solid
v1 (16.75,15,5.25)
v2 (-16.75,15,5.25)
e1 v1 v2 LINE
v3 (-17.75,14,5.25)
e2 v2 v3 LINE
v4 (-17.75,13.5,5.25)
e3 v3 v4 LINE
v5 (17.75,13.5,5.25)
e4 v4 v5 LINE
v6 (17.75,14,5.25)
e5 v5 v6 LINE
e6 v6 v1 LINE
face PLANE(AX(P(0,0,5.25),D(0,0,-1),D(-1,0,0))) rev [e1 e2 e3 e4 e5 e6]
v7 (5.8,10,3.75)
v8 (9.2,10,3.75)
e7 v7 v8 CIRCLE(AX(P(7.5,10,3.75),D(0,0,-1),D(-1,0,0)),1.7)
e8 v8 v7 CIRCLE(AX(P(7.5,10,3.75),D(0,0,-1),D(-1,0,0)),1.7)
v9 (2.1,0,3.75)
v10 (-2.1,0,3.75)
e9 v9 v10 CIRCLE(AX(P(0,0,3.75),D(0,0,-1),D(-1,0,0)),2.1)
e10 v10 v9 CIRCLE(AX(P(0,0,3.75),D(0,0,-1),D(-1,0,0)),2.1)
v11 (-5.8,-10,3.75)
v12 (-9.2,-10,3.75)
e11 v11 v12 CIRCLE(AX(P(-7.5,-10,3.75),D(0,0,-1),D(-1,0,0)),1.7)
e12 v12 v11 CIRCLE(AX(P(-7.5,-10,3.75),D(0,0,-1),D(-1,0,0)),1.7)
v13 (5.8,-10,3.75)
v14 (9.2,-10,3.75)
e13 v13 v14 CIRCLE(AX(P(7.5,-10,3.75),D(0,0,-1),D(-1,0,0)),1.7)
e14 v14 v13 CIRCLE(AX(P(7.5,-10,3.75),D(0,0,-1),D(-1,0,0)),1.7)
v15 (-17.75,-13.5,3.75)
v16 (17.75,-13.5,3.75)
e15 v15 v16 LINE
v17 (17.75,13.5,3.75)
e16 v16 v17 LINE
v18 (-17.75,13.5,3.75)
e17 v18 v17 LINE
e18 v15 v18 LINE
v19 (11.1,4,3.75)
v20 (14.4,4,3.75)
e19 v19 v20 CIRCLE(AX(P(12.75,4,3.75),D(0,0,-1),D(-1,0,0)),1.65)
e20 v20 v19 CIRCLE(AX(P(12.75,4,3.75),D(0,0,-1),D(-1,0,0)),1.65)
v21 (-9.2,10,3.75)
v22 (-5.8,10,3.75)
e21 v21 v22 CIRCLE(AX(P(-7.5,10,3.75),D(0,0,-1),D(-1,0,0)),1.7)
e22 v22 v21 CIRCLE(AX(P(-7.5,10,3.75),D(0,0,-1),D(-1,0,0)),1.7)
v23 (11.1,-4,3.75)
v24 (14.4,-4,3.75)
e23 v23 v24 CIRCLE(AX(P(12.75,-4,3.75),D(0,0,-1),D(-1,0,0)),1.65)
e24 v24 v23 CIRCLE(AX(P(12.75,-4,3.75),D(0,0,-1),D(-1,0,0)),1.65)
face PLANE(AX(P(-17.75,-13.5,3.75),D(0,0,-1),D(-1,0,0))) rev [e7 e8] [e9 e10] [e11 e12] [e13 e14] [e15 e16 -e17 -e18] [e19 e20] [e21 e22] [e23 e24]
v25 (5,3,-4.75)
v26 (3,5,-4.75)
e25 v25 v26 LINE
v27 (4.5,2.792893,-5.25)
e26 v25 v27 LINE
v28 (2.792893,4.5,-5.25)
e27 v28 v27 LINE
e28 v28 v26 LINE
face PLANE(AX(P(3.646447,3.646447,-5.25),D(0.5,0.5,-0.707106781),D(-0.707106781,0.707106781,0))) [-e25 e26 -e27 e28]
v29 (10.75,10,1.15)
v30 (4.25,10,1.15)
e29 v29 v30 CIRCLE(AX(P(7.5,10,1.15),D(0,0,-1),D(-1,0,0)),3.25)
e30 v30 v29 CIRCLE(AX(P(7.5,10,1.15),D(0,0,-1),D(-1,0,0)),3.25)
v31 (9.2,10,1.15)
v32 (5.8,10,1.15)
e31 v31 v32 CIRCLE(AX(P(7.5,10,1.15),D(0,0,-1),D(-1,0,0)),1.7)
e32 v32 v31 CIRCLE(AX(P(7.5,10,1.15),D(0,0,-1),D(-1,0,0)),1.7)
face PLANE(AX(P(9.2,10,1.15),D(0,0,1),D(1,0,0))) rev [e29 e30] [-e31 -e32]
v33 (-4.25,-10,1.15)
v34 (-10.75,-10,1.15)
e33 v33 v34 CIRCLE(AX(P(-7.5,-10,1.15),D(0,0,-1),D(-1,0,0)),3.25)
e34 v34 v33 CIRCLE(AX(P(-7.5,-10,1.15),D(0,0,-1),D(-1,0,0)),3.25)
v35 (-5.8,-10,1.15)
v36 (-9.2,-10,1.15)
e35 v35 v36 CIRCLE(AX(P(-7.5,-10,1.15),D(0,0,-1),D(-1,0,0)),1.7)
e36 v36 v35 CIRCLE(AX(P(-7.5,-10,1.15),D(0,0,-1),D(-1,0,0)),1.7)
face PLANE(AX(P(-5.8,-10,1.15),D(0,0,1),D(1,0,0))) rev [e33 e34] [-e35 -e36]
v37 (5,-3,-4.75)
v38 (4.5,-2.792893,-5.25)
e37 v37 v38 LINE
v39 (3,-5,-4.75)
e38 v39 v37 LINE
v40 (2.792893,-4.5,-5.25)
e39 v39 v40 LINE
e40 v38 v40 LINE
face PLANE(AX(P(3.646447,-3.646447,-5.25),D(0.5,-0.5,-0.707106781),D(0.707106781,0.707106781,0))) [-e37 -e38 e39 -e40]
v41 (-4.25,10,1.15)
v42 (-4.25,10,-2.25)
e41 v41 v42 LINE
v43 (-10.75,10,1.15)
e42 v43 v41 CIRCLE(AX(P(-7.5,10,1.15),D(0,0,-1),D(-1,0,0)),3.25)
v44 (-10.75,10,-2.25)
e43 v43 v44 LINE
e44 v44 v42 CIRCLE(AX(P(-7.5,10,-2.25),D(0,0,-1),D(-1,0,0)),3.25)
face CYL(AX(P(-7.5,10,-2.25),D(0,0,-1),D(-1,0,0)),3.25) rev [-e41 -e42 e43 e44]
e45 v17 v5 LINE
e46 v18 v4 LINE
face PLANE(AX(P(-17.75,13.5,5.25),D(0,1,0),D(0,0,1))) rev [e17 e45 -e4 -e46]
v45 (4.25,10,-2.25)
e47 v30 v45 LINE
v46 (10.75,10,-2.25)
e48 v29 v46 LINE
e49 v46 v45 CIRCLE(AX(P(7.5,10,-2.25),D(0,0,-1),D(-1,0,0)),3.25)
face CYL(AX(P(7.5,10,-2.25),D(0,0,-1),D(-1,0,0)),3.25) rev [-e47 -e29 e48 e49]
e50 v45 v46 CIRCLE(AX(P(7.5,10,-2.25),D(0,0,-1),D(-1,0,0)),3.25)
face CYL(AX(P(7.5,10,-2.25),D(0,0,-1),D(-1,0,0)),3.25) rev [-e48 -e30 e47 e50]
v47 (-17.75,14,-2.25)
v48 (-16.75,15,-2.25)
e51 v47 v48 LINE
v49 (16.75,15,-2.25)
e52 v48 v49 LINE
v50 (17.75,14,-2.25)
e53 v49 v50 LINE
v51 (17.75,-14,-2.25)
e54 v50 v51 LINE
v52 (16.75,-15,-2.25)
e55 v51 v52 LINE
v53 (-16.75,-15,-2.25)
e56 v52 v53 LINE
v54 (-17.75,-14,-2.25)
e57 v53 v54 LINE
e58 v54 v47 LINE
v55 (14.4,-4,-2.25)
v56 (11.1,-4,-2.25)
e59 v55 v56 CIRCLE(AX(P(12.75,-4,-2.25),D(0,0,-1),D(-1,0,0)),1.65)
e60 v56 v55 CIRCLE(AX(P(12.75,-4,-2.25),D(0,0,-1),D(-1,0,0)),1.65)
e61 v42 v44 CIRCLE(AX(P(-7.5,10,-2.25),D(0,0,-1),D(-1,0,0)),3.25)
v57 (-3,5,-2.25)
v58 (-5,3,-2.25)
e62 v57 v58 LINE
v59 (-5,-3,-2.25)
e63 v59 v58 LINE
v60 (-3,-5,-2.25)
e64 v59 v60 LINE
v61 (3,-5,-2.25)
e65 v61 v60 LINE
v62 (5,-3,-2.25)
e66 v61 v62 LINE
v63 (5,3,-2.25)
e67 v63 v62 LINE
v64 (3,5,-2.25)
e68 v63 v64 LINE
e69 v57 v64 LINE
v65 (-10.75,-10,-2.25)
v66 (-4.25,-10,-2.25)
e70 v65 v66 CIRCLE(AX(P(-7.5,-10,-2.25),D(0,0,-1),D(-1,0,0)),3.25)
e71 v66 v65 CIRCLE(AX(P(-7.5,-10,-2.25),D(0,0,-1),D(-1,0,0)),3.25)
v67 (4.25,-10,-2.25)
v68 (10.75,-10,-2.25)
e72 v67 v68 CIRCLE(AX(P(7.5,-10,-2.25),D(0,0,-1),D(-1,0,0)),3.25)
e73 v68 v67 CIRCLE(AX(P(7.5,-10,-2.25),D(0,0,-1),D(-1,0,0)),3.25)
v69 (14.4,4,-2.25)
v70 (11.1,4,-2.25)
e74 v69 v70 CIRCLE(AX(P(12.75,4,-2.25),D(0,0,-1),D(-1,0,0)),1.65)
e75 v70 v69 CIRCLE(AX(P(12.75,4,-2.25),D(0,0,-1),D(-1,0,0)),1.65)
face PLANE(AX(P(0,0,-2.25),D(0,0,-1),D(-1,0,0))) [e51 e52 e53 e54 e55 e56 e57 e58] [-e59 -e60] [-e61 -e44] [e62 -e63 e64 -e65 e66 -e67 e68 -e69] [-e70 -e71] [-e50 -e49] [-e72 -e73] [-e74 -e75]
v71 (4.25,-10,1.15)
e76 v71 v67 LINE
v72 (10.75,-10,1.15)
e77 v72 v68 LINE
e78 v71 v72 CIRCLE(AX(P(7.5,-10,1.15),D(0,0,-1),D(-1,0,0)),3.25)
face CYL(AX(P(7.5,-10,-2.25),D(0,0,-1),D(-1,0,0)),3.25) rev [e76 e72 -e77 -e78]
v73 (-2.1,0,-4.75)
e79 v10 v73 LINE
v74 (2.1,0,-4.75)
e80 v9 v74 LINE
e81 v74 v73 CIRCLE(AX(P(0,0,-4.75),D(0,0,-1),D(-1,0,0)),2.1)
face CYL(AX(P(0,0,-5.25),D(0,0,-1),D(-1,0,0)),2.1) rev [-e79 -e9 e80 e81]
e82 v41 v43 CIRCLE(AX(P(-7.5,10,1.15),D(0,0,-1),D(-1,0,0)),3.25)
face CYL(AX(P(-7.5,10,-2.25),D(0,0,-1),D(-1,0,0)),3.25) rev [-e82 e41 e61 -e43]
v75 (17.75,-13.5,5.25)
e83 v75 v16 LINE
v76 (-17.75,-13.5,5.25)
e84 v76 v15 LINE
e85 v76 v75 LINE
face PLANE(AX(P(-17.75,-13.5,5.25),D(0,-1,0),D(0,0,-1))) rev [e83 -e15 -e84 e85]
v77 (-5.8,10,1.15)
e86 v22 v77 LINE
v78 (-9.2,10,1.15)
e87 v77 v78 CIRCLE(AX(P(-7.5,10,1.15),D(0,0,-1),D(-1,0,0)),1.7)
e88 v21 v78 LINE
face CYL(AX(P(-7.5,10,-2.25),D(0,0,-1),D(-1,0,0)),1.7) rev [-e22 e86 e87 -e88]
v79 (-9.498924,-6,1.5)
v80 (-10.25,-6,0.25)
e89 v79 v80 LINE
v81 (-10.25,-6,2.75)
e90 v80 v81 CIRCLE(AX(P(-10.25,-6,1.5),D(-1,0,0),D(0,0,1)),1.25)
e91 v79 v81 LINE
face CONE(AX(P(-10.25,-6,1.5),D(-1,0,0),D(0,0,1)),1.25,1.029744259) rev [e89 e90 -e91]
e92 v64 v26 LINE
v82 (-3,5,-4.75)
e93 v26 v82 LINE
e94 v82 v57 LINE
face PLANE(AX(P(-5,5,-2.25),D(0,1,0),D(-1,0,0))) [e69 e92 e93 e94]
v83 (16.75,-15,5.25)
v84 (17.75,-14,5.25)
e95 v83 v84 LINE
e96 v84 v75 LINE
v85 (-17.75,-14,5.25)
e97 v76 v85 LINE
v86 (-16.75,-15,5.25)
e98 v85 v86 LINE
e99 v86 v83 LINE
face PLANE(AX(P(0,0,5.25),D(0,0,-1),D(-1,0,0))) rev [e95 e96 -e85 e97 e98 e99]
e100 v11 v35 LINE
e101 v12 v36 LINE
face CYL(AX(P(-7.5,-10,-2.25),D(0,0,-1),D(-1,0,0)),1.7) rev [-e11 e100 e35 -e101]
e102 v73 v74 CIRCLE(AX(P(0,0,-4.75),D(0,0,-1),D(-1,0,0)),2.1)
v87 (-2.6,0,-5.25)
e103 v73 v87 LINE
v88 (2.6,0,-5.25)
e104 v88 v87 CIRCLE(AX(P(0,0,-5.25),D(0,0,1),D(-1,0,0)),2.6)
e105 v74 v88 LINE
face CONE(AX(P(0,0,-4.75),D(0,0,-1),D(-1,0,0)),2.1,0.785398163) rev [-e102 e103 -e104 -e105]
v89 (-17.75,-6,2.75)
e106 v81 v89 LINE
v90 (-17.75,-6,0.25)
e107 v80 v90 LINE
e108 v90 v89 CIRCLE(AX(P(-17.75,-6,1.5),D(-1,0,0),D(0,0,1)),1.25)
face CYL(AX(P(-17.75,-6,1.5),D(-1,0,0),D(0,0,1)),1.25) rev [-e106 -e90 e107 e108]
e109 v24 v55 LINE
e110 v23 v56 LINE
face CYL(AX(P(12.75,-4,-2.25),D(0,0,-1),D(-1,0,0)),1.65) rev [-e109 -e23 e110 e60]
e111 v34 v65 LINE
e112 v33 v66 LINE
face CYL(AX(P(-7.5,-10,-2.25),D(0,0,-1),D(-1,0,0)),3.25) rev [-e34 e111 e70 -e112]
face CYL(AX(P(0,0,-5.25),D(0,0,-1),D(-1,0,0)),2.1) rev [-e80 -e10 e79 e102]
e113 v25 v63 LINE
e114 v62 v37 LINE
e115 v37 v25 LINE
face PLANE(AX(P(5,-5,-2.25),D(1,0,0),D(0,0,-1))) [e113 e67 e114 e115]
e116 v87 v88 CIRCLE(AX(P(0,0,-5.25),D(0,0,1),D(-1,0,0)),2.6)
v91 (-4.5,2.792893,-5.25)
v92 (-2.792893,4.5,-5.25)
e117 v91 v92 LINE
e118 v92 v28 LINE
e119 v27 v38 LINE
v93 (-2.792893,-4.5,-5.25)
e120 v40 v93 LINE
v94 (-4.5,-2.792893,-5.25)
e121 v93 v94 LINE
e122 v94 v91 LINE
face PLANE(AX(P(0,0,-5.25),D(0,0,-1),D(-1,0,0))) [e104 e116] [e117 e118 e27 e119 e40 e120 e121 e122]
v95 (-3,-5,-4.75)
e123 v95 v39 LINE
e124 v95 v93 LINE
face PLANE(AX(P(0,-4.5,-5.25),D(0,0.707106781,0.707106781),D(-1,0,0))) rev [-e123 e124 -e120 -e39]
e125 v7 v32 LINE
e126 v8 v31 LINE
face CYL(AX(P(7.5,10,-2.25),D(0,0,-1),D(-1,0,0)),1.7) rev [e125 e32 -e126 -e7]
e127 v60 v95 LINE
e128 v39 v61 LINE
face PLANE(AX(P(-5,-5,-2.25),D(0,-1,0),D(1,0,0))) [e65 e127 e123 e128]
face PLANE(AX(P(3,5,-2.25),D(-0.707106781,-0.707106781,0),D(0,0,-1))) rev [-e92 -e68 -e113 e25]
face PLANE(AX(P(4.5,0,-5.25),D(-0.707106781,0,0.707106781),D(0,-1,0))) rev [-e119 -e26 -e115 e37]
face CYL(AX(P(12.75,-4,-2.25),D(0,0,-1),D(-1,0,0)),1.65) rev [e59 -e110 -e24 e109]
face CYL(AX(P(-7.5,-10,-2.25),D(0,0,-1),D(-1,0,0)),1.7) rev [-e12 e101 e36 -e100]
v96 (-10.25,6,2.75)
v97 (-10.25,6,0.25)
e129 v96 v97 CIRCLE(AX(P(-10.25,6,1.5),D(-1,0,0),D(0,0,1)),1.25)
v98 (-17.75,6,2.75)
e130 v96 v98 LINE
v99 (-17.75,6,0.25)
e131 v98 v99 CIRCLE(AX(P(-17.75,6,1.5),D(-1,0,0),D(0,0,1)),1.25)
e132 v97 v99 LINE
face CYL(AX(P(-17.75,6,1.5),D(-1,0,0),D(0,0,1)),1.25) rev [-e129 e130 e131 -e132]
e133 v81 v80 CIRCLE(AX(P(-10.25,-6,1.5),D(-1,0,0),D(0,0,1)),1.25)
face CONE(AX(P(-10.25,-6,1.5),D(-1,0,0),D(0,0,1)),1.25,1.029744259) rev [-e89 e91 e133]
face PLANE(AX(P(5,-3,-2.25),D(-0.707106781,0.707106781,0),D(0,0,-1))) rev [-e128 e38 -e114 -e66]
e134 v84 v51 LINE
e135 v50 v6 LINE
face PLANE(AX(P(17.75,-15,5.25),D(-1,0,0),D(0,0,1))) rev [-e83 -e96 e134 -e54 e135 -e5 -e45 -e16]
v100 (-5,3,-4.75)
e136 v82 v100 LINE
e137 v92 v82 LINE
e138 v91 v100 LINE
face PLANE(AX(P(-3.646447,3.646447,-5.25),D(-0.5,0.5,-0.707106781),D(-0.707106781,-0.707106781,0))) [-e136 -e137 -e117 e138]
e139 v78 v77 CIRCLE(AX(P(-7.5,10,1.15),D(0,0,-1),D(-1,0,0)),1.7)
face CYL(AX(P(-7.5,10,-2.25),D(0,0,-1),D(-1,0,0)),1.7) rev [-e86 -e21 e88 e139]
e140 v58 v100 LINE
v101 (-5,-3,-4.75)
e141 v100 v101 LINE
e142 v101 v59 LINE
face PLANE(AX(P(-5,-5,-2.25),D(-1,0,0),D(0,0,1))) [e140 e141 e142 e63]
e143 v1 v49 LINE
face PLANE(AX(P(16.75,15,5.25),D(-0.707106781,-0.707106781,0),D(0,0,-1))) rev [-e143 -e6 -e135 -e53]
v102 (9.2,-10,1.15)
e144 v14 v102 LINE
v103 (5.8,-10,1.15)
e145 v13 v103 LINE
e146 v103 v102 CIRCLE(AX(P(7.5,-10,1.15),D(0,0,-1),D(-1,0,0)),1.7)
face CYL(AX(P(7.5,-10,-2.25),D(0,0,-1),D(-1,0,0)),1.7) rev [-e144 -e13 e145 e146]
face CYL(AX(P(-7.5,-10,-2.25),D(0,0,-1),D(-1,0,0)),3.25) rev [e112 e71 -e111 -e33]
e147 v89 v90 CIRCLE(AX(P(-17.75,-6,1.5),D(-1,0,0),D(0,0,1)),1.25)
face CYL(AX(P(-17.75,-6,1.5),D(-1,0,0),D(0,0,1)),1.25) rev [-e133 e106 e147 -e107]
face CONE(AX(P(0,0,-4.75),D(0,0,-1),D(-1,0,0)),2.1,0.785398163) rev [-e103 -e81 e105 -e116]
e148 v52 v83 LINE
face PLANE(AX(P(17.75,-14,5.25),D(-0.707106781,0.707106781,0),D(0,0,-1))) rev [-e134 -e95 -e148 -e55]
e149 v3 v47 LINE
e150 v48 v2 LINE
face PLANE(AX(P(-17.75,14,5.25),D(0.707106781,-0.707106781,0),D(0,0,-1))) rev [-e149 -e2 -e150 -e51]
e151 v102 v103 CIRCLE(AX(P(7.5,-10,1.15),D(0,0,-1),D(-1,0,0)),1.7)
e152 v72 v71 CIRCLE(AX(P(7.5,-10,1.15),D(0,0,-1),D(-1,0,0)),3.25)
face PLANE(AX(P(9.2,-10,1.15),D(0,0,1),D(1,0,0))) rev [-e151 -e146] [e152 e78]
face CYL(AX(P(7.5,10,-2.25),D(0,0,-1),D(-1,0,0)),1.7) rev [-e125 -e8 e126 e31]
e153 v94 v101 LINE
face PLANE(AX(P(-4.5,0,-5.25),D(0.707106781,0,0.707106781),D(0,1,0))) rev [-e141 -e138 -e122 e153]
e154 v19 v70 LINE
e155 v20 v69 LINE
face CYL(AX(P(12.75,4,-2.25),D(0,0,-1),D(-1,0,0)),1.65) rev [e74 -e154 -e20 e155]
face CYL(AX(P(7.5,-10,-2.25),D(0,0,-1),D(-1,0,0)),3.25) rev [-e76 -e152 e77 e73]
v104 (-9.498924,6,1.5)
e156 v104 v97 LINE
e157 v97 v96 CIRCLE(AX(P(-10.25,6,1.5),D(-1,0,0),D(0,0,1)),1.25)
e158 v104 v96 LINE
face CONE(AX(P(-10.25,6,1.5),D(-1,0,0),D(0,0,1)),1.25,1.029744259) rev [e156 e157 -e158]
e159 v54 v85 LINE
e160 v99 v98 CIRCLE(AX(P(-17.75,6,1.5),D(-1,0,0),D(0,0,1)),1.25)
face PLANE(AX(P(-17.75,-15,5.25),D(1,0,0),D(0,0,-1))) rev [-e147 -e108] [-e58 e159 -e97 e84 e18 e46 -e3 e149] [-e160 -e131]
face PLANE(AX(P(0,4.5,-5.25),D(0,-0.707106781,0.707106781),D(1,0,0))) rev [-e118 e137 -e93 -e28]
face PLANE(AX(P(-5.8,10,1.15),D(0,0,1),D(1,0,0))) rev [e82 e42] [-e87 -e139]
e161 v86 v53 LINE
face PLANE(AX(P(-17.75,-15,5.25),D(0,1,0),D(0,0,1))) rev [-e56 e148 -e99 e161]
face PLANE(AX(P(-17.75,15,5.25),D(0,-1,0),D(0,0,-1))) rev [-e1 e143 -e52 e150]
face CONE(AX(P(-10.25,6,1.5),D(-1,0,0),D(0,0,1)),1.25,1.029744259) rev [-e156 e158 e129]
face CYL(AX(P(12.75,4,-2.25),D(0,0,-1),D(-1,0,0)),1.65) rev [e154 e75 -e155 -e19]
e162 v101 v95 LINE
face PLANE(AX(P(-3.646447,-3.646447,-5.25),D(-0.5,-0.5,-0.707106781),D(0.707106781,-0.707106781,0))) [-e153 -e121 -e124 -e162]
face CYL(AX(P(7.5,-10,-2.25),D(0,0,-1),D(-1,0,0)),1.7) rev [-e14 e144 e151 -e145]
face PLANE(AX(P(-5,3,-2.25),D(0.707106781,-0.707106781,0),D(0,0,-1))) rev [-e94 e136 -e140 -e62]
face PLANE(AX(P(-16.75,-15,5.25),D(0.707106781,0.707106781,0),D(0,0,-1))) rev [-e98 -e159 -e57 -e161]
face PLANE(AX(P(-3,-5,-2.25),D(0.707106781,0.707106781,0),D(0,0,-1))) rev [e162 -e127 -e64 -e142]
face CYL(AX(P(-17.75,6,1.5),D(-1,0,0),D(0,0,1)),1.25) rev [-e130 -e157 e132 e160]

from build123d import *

# Parameters (mm, degrees)
SKETCH1_W                                           = 35.5
SKETCH1_H                                           = 30
BOSS_EXTRUDE1_DEPTH                                 = 5.25
SKETCH2_W                                           = 1.5
SKETCH2_H                                           = 27
CUT_EXTRUDE1_DEPTH                                  = 39.89489041
M5_TAPPED_HOLE1_D                                   = 4.2
M5_TAPPED_HOLE1_DEPTH                               = 12.4
M5_TAPPED_HOLE1_TIP                                 = 1.2618073
SKETCH14_OUTSIDE_W                                  = 47.03
SKETCH14_OUTSIDE_H                                  = 41.53
SKETCH14_OUTSIDE_W_2                                = 10
SKETCH14_OUTSIDE_H_2                                = 10
CUT_EXTRUDE4_DEPTH                                  = 3
CHAMFER1_SIZE                                       = 2
M4_TAPPED_HOLE3_D                                   = 3.3
M4_TAPPED_HOLE3_DEPTH                               = 10.1
M4_TAPPED_HOLE3_TIP                                 = 0.991420021
CHAMFER2_SIZE                                       = 1
CHAMFER3_SIZE                                       = 0.5
CBORE_FOR_M3_HEX_SOCKET_HEAD_CAP_SCREW1_D           = 3.4
CBORE_FOR_M3_HEX_SOCKET_HEAD_CAP_SCREW1_CBORE_D     = 6.5
CBORE_FOR_M3_HEX_SOCKET_HEAD_CAP_SCREW1_CBORE_DEPTH = 3.4
M3_TAPPED_HOLE1_D                                   = 2.5
M3_TAPPED_HOLE1_DEPTH                               = 7.5
M3_TAPPED_HOLE1_TIP                                 = 0.751075774


with BuildPart() as part:
    # Sketch1 → Boss-Extrude1 (new, symmetric)
    with BuildSketch(Plane.XY):
        Rectangle(SKETCH1_W, SKETCH1_H)
    extrude(amount=BOSS_EXTRUDE1_DEPTH, both=True)

    # Sketch2 → Cut-Extrude1 (cut, through all)
    with BuildSketch(Plane(origin=(17.75, 0, 0), x_dir=(0, 0, -1), z_dir=(1, 0, 0))):
        with Locations((-4.5, 0)):
            Rectangle(SKETCH2_W, SKETCH2_H)
    extrude(amount=-CUT_EXTRUDE1_DEPTH, mode=Mode.SUBTRACT)

    # M5 Tapped Hole1
    with Locations(Plane(origin=(0, 0, -5.25), x_dir=(-1, 0, 0), z_dir=(0, 0, -1))):
        with Locations((0, 0)):
            Hole(M5_TAPPED_HOLE1_D / 2, depth=M5_TAPPED_HOLE1_DEPTH)
            with Locations((0, 0, -(M5_TAPPED_HOLE1_DEPTH + M5_TAPPED_HOLE1_TIP / 2))):  # 118° drill point
                Cone(0, M5_TAPPED_HOLE1_D / 2, M5_TAPPED_HOLE1_TIP, mode=Mode.SUBTRACT)

    # Sketch14 outside → Cut-Extrude4 (cut)
    with BuildSketch(Plane(origin=(0, 0, -5.25), x_dir=(-1, 0, 0), z_dir=(0, 0, -1))):
        Rectangle(SKETCH14_OUTSIDE_W, SKETCH14_OUTSIDE_H)
        Rectangle(SKETCH14_OUTSIDE_W_2, SKETCH14_OUTSIDE_H_2, mode=Mode.SUBTRACT)
    extrude(amount=-CUT_EXTRUDE4_DEPTH, mode=Mode.SUBTRACT)

    # Chamfer1
    chamfer1_edges = [part.edges().sort_by_distance(p)[0] for p in [
        (5, 5, -3.75),
        (-5, 5, -3.75),
        (-5, -5, -3.75),
        (5, -5, -3.75),
    ]]
    chamfer(chamfer1_edges, length=CHAMFER1_SIZE)

    # M4 Tapped Hole3
    with Locations(Plane(origin=(0, 0, -2.25), x_dir=(-1, 0, 0), z_dir=(0, 0, -1))):
        with Locations((-12.75, 4), (-12.75, -4)):
            Hole(M4_TAPPED_HOLE3_D / 2, depth=M4_TAPPED_HOLE3_DEPTH)
            with Locations((0, 0, -(M4_TAPPED_HOLE3_DEPTH + M4_TAPPED_HOLE3_TIP / 2))):  # 118° drill point
                Cone(0, M4_TAPPED_HOLE3_D / 2, M4_TAPPED_HOLE3_TIP, mode=Mode.SUBTRACT)

    # Chamfer2
    chamfer2_edges = [part.edges().sort_by_distance(p)[0] for p in [
        (17.75, -15, 1.5),
        (-17.75, -15, 1.5),
        (-17.75, 15, 1.5),
        (17.75, 15, 1.5),
    ]]
    chamfer(chamfer2_edges, length=CHAMFER2_SIZE)

    # Chamfer3
    chamfer3_edges = [part.edges().sort_by_distance(p)[0] for p in [
        (-2.1, 0, -5.25),
        (5, 0, -5.25),
        (0, 5, -5.25),
        (0, -5, -5.25),
        (-5, 0, -5.25),
        (-4, -4, -5.25),
        (-4, 4, -5.25),
        (4, 4, -5.25),
        (4, -4, -5.25),
    ]]
    chamfer(chamfer3_edges, length=CHAMFER3_SIZE)

    # CBORE for M3 Hex Socket Head Cap Screw1 (through all)
    with Locations(Plane(origin=(0, 0, -2.25), x_dir=(-1, 0, 0), z_dir=(0, 0, -1))):
        with Locations((-7.5, 10), (7.5, 10), (7.5, -10), (-7.5, -10)):
            CounterBoreHole(CBORE_FOR_M3_HEX_SOCKET_HEAD_CAP_SCREW1_D / 2, CBORE_FOR_M3_HEX_SOCKET_HEAD_CAP_SCREW1_CBORE_D / 2, CBORE_FOR_M3_HEX_SOCKET_HEAD_CAP_SCREW1_CBORE_DEPTH)

    # M3 Tapped Hole1
    with Locations(Plane(origin=(-17.75, -2.75, 0), x_dir=(0, -1, 0), z_dir=(-1, 0, 0))):
        with Locations((3.25, 1.5), (-8.75, 1.5)):
            Hole(M3_TAPPED_HOLE1_D / 2, depth=M3_TAPPED_HOLE1_DEPTH)
            with Locations((0, 0, -(M3_TAPPED_HOLE1_DEPTH + M3_TAPPED_HOLE1_TIP / 2))):  # 118° drill point
                Cone(0, M3_TAPPED_HOLE1_D / 2, M3_TAPPED_HOLE1_TIP, mode=Mode.SUBTRACT)


solid = part.part
